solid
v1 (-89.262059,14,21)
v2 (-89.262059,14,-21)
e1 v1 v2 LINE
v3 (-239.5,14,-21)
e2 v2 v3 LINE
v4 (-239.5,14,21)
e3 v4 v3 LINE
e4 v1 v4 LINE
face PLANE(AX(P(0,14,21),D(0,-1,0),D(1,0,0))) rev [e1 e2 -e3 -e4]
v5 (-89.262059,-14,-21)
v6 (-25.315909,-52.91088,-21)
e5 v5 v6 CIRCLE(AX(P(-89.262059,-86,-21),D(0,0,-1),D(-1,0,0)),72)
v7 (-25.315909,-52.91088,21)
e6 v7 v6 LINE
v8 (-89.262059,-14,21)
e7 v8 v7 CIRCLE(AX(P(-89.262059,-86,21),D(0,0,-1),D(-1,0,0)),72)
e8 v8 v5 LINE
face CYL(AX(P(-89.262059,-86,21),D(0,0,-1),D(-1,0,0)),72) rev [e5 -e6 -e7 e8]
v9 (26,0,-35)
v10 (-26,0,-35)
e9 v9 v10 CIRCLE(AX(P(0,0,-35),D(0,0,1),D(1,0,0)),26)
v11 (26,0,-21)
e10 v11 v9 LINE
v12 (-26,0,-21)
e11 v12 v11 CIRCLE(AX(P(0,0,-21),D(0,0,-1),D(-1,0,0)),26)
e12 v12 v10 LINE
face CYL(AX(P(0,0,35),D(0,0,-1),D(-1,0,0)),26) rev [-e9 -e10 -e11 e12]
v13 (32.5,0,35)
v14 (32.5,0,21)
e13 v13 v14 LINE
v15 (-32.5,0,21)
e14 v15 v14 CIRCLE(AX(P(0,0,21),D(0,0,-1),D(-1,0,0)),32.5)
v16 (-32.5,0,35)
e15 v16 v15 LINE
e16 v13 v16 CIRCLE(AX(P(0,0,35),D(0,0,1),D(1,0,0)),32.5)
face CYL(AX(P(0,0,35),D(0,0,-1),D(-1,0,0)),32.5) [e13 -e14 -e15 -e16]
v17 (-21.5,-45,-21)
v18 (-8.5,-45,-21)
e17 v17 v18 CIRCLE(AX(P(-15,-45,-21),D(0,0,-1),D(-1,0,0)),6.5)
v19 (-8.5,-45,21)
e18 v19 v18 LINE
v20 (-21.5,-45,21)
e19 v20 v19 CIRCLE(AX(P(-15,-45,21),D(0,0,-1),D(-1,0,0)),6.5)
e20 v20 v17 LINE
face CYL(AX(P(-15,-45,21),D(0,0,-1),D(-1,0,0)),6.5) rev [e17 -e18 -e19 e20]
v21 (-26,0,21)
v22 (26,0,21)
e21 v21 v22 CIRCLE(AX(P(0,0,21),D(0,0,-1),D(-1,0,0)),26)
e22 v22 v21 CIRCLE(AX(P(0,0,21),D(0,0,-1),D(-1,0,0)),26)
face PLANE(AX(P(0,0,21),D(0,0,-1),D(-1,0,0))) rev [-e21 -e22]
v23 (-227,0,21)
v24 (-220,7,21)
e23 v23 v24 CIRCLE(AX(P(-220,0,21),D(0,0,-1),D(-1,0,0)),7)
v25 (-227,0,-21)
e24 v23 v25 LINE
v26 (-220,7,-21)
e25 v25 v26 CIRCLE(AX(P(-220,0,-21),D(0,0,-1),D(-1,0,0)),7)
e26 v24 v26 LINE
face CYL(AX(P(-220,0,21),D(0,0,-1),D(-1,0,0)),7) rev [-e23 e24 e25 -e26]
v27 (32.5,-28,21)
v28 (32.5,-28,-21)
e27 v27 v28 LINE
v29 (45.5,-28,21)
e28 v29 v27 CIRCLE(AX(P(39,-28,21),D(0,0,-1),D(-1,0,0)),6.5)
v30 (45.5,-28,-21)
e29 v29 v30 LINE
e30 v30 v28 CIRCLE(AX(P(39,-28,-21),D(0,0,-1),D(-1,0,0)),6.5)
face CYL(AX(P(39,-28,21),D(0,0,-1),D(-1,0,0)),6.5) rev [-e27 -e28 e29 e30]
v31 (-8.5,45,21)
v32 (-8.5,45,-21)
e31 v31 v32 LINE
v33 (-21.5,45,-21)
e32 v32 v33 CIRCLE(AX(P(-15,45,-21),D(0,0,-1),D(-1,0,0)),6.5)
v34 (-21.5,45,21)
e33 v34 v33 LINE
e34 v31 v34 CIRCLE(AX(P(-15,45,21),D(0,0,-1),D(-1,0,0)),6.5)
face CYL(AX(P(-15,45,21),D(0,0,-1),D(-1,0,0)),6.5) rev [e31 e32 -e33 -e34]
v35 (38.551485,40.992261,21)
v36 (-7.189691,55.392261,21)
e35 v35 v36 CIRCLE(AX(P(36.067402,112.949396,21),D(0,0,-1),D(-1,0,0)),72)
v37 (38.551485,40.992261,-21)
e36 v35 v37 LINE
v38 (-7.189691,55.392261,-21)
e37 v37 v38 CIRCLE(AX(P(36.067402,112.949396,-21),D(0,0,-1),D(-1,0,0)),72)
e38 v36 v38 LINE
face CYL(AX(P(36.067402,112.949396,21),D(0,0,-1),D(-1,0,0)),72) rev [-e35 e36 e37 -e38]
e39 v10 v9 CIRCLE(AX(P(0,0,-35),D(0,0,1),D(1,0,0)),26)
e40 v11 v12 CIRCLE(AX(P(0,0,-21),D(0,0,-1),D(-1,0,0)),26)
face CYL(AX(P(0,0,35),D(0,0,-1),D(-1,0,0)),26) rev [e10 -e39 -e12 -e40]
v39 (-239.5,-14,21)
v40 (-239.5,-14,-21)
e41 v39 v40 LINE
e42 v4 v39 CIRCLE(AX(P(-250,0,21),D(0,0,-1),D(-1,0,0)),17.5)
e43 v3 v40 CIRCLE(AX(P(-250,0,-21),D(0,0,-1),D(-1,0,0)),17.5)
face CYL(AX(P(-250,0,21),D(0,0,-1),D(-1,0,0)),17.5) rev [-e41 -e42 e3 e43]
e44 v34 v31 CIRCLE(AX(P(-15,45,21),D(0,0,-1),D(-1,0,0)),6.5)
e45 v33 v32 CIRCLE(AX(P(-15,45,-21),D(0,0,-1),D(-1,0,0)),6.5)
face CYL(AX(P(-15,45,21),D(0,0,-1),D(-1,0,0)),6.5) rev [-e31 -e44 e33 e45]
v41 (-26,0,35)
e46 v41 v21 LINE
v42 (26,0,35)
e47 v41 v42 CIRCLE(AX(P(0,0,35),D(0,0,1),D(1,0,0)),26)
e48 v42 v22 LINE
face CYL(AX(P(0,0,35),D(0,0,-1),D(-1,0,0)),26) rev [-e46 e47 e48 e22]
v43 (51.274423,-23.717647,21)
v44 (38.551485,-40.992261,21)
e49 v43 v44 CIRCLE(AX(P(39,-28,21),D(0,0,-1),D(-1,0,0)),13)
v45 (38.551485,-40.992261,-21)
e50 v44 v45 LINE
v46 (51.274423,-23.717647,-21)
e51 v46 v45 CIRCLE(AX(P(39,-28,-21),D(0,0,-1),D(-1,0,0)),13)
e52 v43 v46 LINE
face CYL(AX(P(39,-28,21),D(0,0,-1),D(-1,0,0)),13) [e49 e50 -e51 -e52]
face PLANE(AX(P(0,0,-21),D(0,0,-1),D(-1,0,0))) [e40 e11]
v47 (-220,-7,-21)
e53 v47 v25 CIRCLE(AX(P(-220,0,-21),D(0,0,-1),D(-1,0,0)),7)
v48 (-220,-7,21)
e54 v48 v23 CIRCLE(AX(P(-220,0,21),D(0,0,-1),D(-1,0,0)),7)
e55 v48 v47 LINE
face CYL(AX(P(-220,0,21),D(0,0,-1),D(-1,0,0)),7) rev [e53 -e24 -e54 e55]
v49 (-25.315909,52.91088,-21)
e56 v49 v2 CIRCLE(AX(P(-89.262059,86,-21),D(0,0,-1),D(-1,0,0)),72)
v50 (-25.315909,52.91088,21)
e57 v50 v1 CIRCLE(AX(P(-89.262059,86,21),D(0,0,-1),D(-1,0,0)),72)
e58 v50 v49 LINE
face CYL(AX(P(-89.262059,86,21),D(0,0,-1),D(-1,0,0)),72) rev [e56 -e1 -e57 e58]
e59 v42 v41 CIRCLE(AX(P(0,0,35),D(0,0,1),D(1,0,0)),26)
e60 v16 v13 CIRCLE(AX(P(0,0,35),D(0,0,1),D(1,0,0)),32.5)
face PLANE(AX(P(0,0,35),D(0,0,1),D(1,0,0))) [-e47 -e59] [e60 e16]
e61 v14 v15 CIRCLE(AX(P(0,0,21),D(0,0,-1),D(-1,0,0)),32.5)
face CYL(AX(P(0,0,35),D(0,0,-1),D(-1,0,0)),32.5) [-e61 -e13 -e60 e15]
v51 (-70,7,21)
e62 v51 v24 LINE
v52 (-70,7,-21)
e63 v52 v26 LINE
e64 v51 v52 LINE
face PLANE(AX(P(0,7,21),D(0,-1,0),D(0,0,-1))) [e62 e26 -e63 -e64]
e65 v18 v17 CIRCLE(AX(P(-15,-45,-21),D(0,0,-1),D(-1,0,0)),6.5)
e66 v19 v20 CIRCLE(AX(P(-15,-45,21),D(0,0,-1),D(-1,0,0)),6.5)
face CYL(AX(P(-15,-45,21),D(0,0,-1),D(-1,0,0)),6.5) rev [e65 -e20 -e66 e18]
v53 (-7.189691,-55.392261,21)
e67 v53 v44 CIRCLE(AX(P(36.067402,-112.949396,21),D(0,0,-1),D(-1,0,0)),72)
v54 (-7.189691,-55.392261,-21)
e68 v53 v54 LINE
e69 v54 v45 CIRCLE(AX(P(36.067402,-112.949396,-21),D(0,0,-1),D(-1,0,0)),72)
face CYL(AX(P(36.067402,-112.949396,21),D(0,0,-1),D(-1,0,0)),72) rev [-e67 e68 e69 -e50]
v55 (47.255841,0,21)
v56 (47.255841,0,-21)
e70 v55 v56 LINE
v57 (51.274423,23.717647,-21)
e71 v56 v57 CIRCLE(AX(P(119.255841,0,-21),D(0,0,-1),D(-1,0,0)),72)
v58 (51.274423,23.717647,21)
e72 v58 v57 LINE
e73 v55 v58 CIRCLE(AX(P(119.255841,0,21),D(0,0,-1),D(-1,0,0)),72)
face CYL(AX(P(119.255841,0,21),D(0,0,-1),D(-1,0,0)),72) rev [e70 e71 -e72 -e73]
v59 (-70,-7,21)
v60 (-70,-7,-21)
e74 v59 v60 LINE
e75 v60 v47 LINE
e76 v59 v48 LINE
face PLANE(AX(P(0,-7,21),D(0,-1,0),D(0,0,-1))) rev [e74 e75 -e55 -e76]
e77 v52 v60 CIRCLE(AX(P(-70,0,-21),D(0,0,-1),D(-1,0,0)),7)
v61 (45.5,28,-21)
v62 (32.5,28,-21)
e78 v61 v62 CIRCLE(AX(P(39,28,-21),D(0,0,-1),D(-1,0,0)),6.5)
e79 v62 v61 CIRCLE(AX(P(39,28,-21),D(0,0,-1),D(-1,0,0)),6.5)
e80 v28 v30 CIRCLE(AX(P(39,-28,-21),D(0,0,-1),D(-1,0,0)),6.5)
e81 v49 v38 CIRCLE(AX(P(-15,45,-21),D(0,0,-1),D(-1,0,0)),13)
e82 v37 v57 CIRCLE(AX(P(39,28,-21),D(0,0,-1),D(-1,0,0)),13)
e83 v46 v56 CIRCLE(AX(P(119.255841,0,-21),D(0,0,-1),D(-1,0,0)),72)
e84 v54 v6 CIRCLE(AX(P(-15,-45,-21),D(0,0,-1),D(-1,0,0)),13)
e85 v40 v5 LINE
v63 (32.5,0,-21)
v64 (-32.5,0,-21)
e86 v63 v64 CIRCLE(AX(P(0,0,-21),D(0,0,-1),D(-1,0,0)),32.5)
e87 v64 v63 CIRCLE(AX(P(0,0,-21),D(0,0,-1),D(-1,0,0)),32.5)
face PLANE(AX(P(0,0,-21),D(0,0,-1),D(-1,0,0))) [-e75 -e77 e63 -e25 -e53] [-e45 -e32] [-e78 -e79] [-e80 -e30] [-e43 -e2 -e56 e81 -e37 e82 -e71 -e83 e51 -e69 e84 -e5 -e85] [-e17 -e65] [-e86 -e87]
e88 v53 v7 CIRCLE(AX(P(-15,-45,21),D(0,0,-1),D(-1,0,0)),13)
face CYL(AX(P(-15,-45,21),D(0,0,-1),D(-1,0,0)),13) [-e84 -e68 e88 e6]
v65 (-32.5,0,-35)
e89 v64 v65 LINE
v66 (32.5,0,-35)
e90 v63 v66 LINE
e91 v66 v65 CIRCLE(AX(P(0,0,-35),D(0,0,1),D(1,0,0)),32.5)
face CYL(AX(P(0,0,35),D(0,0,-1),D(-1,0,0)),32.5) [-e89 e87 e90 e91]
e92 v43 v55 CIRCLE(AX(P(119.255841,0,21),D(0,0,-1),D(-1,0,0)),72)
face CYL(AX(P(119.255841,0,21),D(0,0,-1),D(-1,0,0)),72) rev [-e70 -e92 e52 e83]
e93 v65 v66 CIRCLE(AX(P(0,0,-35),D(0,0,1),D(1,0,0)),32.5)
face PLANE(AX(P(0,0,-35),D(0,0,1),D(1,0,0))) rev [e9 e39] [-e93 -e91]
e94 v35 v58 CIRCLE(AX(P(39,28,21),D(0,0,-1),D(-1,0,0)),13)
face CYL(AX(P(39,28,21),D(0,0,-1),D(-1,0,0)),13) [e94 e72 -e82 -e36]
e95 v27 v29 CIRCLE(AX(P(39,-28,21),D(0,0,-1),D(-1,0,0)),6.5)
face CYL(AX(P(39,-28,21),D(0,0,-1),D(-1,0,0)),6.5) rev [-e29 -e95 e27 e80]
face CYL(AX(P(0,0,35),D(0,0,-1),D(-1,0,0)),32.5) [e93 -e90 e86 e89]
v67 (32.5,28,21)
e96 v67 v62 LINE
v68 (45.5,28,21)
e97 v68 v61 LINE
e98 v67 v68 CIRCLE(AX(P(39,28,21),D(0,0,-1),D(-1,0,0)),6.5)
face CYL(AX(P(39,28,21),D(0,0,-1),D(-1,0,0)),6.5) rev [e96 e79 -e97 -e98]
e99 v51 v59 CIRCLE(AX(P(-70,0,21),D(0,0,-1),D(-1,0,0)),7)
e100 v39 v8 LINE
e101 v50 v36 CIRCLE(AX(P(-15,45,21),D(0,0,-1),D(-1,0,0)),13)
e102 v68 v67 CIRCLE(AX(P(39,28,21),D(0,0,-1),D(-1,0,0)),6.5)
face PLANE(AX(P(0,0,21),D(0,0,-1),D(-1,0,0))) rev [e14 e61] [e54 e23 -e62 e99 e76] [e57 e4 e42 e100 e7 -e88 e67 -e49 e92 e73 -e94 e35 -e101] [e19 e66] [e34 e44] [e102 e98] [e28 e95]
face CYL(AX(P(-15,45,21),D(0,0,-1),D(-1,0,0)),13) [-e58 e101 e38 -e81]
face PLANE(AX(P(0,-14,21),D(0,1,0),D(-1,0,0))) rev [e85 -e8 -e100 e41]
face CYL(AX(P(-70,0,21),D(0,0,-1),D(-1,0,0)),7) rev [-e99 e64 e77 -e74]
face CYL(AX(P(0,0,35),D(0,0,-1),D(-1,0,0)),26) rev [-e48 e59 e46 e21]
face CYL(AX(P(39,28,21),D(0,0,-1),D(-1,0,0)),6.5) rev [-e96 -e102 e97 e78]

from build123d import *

# Parameters (mm, degrees)
HUB_BLOCK_SKETCH_R   = 32.5
HUB_BLOCK_SKETCH_R_2 = 26
HUB_BLOCK_DEPTH      = 35
ARM_PROFILE_SKETCH_R = 6.5
ARM_BODY_DEPTH       = 42


with BuildPart() as part:
    # Hub Block Sketch → Hub Block (new, symmetric)
    with BuildSketch(Plane.XY):
        Circle(HUB_BLOCK_SKETCH_R)
        Circle(HUB_BLOCK_SKETCH_R_2, mode=Mode.SUBTRACT)
    extrude(amount=HUB_BLOCK_DEPTH, both=True)

    # Arm Profile Sketch → Arm Body (add)
    with BuildSketch(Plane(origin=(0, 0, -21), x_dir=(-1, 0, 0), z_dir=(0, 0, -1))):
        with BuildLine():
            ThreePointArc((89.262059242, -14), (51.834907578, -24.492209287), (25.315908922, -52.910880046))
            ThreePointArc((25.315908922, -52.910880046), (16.763184773, -57.879874978), (7.189691393, -55.392260556))
            ThreePointArc((7.189691393, -55.392260556), (-14.44681941, -44.272249892), (-38.551485077, -40.992260556))
            ThreePointArc((-38.551485077, -40.992260556), (-49.467382276, -35.70933903), (-51.274422727, -23.717647059))
            ThreePointArc((-51.274422727, -23.717647059), (-47.255840909, 0), (-51.274422727, 23.717647059))
            ThreePointArc((-51.274422727, 23.717647059), (-49.467382276, 35.70933903), (-38.551485077, 40.992260556))
            ThreePointArc((-38.551485077, 40.992260556), (-14.44681941, 44.272249892), (7.189691393, 55.392260556))
            ThreePointArc((7.189691393, 55.392260556), (16.763184773, 57.879874978), (25.315908922, 52.910880046))
            ThreePointArc((25.315908922, 52.910880046), (51.834907578, 24.492209287), (89.262059242, 14))
            Line((89.262059242, 14), (239.5, 14))
            ThreePointArc((239.5, 14), (232.5, 0), (239.5, -14))
            Line((239.5, -14), (89.262059242, -14))
        make_face()
        with Locations((15, -45)):
            Circle(ARM_PROFILE_SKETCH_R, mode=Mode.SUBTRACT)
        with Locations((15, 45)):
            Circle(ARM_PROFILE_SKETCH_R, mode=Mode.SUBTRACT)
        with Locations((-39, -28)):
            Circle(ARM_PROFILE_SKETCH_R, mode=Mode.SUBTRACT)
        with Locations((-39, 28)):
            Circle(ARM_PROFILE_SKETCH_R, mode=Mode.SUBTRACT)
        with BuildLine():
            ThreePointArc((220, -7), (227, 0), (220, 7))
            Line((220, 7), (70, 7))
            ThreePointArc((70, 7), (63, 0), (70, -7))
            Line((70, -7), (220, -7))
        make_face(mode=Mode.SUBTRACT)
    extrude(amount=-ARM_BODY_DEPTH)


solid = part.part
